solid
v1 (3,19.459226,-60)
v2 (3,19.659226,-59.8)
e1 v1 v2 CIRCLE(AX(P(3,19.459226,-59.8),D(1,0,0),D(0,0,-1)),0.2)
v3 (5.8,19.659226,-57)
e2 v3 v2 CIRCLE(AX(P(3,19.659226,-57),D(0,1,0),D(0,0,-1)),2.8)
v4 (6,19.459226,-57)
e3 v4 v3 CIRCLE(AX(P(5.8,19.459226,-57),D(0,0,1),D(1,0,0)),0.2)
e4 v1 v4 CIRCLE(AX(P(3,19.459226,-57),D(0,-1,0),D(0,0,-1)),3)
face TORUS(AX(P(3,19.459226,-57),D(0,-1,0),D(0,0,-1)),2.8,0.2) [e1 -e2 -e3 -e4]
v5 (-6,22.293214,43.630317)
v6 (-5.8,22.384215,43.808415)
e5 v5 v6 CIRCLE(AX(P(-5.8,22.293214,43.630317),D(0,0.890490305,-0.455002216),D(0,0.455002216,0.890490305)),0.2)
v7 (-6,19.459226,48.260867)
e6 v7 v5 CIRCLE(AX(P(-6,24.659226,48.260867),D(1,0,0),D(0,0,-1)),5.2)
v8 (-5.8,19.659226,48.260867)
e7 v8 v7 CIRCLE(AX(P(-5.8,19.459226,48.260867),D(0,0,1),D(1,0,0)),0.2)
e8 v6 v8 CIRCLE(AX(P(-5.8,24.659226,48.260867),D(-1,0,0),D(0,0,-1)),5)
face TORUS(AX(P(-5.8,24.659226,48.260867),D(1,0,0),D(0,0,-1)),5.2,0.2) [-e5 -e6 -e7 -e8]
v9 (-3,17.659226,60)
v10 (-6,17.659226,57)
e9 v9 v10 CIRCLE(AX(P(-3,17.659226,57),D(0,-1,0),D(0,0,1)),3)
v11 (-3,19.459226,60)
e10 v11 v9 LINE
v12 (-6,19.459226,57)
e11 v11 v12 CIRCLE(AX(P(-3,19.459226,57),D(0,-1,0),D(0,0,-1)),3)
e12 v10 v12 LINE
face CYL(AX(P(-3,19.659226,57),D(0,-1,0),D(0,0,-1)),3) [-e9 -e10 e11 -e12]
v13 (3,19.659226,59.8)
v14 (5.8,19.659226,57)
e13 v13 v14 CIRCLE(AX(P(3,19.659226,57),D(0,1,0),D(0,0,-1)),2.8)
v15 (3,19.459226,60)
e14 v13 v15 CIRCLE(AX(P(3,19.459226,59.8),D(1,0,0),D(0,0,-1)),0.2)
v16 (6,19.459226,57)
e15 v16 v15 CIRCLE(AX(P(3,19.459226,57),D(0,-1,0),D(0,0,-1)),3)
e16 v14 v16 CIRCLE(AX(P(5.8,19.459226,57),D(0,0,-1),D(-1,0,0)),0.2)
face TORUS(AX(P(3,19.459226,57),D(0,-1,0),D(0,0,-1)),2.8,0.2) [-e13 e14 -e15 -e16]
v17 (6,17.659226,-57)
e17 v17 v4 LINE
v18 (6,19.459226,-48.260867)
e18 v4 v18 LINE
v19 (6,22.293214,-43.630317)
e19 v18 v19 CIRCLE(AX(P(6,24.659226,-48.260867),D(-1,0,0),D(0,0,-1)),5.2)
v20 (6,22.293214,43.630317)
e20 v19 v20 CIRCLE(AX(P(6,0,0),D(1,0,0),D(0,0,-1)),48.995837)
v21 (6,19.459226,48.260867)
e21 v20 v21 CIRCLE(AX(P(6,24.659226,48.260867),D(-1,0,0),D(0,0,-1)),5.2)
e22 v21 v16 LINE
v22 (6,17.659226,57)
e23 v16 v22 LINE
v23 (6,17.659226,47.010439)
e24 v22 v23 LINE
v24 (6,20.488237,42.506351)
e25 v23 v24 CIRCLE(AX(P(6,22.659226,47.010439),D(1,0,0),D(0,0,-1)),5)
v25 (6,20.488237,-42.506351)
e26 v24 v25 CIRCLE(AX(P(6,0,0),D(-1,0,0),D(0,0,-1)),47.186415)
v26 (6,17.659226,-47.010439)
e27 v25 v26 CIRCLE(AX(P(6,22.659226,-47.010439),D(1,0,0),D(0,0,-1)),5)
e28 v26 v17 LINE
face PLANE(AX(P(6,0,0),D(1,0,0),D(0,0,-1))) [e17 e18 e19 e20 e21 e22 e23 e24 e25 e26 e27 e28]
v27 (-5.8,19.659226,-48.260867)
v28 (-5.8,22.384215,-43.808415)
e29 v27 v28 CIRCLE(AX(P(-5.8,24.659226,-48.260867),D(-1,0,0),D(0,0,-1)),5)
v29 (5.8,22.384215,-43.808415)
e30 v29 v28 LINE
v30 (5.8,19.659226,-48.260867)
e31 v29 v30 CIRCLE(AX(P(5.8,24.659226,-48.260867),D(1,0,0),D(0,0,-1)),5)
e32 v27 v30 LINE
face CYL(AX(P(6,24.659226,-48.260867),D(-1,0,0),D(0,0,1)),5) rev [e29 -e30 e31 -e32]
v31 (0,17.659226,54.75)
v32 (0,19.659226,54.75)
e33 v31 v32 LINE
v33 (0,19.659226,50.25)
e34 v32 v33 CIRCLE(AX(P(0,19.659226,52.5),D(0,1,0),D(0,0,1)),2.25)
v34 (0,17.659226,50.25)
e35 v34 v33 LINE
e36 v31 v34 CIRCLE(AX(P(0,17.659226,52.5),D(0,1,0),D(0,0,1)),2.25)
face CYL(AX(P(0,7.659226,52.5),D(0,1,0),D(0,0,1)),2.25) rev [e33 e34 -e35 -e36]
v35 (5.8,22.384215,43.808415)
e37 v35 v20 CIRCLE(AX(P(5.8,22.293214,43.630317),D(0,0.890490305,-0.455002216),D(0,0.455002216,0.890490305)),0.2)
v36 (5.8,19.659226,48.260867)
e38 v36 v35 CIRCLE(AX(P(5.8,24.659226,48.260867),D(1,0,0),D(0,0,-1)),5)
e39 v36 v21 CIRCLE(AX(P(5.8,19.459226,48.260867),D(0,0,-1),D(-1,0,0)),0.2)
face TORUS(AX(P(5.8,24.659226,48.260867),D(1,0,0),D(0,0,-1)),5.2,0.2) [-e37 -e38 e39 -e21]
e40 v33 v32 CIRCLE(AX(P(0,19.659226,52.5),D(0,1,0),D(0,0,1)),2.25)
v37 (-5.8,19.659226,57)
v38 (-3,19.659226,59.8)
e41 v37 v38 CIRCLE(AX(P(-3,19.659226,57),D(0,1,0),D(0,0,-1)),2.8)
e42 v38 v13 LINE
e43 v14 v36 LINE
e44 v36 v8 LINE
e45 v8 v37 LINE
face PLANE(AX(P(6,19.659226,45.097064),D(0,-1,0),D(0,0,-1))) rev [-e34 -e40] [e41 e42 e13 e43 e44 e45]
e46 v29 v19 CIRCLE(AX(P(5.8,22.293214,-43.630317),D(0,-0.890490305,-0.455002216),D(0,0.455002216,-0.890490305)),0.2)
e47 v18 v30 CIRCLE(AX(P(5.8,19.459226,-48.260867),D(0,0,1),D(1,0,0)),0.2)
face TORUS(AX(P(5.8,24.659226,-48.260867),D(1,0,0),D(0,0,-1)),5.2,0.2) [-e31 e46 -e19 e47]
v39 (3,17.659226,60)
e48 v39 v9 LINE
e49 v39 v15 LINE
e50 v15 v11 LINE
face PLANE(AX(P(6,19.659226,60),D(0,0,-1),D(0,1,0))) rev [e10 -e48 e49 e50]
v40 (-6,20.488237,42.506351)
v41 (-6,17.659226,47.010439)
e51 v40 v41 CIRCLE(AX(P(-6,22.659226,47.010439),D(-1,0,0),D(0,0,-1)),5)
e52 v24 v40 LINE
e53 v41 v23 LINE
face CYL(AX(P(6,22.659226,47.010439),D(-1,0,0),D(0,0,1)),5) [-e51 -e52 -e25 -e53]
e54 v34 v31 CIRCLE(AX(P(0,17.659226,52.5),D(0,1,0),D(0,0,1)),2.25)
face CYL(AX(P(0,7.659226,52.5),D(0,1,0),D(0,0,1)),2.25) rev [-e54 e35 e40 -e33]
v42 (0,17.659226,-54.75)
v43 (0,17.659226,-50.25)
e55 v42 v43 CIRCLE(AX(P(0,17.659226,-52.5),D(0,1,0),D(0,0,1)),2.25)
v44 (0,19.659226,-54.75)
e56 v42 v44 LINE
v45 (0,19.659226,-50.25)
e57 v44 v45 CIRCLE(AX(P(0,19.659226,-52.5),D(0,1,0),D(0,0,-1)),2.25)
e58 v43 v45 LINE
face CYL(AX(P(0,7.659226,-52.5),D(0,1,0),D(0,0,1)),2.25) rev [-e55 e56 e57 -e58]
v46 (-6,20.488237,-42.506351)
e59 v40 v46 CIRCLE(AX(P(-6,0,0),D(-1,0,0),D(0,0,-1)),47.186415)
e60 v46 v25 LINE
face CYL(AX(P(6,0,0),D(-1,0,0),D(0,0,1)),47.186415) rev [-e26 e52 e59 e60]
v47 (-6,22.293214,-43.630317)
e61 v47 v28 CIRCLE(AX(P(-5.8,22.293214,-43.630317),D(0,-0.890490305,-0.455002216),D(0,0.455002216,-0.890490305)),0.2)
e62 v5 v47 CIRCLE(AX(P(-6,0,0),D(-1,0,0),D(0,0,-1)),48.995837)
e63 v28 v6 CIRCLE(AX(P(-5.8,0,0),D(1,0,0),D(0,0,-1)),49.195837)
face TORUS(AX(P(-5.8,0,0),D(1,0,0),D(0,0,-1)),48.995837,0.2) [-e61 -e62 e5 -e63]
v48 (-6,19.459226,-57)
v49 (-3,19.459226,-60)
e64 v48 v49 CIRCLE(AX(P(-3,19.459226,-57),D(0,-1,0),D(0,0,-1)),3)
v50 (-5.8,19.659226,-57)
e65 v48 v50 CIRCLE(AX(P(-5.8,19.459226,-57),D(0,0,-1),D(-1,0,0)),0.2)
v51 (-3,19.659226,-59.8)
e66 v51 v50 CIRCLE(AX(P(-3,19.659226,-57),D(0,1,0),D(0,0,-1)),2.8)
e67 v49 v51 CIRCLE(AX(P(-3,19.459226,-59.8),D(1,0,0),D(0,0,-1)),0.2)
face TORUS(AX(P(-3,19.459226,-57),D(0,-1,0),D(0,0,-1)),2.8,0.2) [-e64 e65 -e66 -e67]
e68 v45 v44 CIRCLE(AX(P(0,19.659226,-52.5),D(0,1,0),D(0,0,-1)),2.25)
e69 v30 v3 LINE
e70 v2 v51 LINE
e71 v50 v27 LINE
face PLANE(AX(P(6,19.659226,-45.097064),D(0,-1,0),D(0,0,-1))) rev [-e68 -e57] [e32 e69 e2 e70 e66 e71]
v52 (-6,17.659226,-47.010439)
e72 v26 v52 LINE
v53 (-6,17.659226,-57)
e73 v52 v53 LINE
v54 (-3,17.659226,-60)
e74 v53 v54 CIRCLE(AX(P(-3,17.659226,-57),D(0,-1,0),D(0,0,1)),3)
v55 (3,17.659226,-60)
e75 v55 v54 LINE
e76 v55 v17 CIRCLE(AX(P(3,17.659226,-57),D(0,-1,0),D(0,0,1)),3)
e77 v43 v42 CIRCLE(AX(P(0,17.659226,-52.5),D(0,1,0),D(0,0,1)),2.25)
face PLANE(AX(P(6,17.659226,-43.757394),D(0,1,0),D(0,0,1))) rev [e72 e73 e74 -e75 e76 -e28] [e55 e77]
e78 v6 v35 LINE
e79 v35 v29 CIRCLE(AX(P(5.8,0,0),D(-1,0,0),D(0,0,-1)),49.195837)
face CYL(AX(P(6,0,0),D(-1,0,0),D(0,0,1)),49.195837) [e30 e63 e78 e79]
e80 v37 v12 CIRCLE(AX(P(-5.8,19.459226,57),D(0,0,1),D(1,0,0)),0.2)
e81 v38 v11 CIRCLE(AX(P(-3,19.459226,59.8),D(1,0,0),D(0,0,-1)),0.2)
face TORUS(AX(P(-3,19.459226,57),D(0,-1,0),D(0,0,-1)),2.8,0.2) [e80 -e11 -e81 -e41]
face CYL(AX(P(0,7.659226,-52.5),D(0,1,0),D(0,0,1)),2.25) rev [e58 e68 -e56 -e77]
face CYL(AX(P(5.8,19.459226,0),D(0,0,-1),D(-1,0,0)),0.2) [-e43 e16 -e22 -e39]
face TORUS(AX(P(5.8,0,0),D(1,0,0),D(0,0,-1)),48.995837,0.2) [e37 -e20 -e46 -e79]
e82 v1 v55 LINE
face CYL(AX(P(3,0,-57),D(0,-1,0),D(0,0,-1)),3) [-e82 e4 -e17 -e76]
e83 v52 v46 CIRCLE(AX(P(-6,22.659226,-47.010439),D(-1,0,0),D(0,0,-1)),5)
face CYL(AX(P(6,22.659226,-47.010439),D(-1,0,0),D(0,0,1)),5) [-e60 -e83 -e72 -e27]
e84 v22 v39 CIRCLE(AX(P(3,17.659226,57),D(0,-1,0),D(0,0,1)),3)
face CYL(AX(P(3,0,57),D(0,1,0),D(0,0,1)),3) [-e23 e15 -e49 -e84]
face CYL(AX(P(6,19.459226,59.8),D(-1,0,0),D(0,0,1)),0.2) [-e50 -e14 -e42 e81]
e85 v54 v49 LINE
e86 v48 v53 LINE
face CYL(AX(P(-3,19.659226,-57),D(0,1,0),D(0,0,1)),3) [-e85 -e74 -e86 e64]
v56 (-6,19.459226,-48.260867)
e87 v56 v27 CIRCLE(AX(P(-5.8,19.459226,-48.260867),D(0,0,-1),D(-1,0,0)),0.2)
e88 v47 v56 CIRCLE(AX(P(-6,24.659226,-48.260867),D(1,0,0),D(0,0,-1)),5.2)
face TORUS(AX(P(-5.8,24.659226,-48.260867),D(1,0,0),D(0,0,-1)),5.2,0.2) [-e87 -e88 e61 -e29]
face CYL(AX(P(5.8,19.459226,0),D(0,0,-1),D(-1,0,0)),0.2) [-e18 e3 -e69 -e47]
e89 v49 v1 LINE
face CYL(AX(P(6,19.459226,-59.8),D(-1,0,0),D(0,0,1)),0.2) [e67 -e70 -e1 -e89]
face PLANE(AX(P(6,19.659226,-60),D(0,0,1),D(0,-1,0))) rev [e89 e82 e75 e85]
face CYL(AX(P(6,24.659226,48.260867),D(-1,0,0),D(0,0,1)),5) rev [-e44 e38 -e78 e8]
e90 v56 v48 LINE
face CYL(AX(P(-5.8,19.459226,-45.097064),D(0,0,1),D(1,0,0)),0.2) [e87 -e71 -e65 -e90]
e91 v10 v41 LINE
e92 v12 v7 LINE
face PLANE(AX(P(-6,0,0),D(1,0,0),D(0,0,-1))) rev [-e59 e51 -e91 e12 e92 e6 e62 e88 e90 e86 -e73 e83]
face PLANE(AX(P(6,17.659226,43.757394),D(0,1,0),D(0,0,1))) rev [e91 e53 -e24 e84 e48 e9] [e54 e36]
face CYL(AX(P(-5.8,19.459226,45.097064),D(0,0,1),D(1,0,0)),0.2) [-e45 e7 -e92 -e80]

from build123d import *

# Parameters (mm, degrees)
EXTRUDE_1_DEPTH     = 6
SKETCH_2_R          = 2.25
CUT_EXTRUDE_1_DEPTH = 12
FILLET_1_R          = 3
FILLET_2_R          = 5
FILLET_3_R          = 5
FILLET_4_R          = 0.2


with BuildPart() as part:
    # 草图1 → 凸台-拉伸1 (new, symmetric)
    with BuildSketch(Plane(origin=(0, 0, 0), x_dir=(0, 0, -1), z_dir=(1, 0, 0))):
        with BuildLine():
            Line((43.757393596, 17.659225719), (60, 17.659225719))
            Line((60, 17.659225719), (60, 19.659225719))
            Line((60, 19.659225719), (45.097063909, 19.659225719))
            ThreePointArc((45.097063909, 19.659225719), (0, 49.195836501), (-45.097063909, 19.659225719))
            Line((-45.097063909, 19.659225719), (-60, 19.659225719))
            Line((-60, 19.659225719), (-60, 17.659225719))
            Line((-60, 17.659225719), (-43.757393596, 17.659225719))
            ThreePointArc((-43.757393596, 17.659225719), (0, 47.186414859), (43.757393596, 17.659225719))
        make_face()
    extrude(amount=EXTRUDE_1_DEPTH, both=True)

    # 草图2 → 切除-拉伸1 (cut)
    with BuildSketch(Plane(origin=(0, 19.659225719, 0), x_dir=(1, 0, 0), z_dir=(0, 1, 0))):
        with Locations(Location((0, -52.5, 0), (0, 0, 270))):
            Circle(SKETCH_2_R)
        with Locations(Location((0, 52.5, 0), (0, 0, 270))):
            Circle(SKETCH_2_R)
    extrude(amount=-CUT_EXTRUDE_1_DEPTH, mode=Mode.SUBTRACT)

    # 圆角1
    fillet_1_edges = [part.edges().sort_by_distance(p)[0] for p in [
        (6, 18.659225719, -60),
        (6, 18.659225719, 60),
        (-6, 18.659225719, 60),
        (-6, 18.659225719, -60),
    ]]
    fillet(fillet_1_edges, radius=FILLET_1_R)

    # 圆角2
    fillet_2_edges = [part.edges().sort_by_distance(p)[0] for p in [
        (0, 19.659225719, 45.097063909),
        (0, 19.659225719, -45.097063909),
    ]]
    fillet(fillet_2_edges, radius=FILLET_2_R)

    # 圆角3
    fillet_3_edges = [part.edges().sort_by_distance(p)[0] for p in [
        (0, 17.659225719, 43.757393596),
        (0, 17.659225719, -43.757393596),
    ]]
    fillet(fillet_3_edges, radius=FILLET_3_R)

    # 圆角4
    fillet_4_edges = [part.edges().sort_by_distance(p)[0] for p in [
        (6, 19.659225719, -52.630433487),
        (0, 19.659225719, 60),
        (-5.121320344, 19.659225719, 59.121320344),
        (5.121320344, 19.659225719, 59.121320344),
        (-6, 19.659225719, -52.630433487),
        (0, 19.659225719, -60),
        (5.121320344, 19.659225719, -59.121320344),
        (-5.121320344, 19.659225719, -59.121320344),
        (-6, 49.195836501, 0),
        (6, 49.195836501, 0),
        (6, 19.659225719, 52.630433487),
        (-6, 19.659225719, 52.630433487),
        (-6, 20.394541943, -45.650795653),
        (6, 20.394541943, -45.650795653),
        (-6, 20.394541943, 45.650795653),
        (6, 20.394541943, 45.650795653),
    ]]
    fillet(fillet_4_edges, radius=FILLET_4_R)


solid = part.part
